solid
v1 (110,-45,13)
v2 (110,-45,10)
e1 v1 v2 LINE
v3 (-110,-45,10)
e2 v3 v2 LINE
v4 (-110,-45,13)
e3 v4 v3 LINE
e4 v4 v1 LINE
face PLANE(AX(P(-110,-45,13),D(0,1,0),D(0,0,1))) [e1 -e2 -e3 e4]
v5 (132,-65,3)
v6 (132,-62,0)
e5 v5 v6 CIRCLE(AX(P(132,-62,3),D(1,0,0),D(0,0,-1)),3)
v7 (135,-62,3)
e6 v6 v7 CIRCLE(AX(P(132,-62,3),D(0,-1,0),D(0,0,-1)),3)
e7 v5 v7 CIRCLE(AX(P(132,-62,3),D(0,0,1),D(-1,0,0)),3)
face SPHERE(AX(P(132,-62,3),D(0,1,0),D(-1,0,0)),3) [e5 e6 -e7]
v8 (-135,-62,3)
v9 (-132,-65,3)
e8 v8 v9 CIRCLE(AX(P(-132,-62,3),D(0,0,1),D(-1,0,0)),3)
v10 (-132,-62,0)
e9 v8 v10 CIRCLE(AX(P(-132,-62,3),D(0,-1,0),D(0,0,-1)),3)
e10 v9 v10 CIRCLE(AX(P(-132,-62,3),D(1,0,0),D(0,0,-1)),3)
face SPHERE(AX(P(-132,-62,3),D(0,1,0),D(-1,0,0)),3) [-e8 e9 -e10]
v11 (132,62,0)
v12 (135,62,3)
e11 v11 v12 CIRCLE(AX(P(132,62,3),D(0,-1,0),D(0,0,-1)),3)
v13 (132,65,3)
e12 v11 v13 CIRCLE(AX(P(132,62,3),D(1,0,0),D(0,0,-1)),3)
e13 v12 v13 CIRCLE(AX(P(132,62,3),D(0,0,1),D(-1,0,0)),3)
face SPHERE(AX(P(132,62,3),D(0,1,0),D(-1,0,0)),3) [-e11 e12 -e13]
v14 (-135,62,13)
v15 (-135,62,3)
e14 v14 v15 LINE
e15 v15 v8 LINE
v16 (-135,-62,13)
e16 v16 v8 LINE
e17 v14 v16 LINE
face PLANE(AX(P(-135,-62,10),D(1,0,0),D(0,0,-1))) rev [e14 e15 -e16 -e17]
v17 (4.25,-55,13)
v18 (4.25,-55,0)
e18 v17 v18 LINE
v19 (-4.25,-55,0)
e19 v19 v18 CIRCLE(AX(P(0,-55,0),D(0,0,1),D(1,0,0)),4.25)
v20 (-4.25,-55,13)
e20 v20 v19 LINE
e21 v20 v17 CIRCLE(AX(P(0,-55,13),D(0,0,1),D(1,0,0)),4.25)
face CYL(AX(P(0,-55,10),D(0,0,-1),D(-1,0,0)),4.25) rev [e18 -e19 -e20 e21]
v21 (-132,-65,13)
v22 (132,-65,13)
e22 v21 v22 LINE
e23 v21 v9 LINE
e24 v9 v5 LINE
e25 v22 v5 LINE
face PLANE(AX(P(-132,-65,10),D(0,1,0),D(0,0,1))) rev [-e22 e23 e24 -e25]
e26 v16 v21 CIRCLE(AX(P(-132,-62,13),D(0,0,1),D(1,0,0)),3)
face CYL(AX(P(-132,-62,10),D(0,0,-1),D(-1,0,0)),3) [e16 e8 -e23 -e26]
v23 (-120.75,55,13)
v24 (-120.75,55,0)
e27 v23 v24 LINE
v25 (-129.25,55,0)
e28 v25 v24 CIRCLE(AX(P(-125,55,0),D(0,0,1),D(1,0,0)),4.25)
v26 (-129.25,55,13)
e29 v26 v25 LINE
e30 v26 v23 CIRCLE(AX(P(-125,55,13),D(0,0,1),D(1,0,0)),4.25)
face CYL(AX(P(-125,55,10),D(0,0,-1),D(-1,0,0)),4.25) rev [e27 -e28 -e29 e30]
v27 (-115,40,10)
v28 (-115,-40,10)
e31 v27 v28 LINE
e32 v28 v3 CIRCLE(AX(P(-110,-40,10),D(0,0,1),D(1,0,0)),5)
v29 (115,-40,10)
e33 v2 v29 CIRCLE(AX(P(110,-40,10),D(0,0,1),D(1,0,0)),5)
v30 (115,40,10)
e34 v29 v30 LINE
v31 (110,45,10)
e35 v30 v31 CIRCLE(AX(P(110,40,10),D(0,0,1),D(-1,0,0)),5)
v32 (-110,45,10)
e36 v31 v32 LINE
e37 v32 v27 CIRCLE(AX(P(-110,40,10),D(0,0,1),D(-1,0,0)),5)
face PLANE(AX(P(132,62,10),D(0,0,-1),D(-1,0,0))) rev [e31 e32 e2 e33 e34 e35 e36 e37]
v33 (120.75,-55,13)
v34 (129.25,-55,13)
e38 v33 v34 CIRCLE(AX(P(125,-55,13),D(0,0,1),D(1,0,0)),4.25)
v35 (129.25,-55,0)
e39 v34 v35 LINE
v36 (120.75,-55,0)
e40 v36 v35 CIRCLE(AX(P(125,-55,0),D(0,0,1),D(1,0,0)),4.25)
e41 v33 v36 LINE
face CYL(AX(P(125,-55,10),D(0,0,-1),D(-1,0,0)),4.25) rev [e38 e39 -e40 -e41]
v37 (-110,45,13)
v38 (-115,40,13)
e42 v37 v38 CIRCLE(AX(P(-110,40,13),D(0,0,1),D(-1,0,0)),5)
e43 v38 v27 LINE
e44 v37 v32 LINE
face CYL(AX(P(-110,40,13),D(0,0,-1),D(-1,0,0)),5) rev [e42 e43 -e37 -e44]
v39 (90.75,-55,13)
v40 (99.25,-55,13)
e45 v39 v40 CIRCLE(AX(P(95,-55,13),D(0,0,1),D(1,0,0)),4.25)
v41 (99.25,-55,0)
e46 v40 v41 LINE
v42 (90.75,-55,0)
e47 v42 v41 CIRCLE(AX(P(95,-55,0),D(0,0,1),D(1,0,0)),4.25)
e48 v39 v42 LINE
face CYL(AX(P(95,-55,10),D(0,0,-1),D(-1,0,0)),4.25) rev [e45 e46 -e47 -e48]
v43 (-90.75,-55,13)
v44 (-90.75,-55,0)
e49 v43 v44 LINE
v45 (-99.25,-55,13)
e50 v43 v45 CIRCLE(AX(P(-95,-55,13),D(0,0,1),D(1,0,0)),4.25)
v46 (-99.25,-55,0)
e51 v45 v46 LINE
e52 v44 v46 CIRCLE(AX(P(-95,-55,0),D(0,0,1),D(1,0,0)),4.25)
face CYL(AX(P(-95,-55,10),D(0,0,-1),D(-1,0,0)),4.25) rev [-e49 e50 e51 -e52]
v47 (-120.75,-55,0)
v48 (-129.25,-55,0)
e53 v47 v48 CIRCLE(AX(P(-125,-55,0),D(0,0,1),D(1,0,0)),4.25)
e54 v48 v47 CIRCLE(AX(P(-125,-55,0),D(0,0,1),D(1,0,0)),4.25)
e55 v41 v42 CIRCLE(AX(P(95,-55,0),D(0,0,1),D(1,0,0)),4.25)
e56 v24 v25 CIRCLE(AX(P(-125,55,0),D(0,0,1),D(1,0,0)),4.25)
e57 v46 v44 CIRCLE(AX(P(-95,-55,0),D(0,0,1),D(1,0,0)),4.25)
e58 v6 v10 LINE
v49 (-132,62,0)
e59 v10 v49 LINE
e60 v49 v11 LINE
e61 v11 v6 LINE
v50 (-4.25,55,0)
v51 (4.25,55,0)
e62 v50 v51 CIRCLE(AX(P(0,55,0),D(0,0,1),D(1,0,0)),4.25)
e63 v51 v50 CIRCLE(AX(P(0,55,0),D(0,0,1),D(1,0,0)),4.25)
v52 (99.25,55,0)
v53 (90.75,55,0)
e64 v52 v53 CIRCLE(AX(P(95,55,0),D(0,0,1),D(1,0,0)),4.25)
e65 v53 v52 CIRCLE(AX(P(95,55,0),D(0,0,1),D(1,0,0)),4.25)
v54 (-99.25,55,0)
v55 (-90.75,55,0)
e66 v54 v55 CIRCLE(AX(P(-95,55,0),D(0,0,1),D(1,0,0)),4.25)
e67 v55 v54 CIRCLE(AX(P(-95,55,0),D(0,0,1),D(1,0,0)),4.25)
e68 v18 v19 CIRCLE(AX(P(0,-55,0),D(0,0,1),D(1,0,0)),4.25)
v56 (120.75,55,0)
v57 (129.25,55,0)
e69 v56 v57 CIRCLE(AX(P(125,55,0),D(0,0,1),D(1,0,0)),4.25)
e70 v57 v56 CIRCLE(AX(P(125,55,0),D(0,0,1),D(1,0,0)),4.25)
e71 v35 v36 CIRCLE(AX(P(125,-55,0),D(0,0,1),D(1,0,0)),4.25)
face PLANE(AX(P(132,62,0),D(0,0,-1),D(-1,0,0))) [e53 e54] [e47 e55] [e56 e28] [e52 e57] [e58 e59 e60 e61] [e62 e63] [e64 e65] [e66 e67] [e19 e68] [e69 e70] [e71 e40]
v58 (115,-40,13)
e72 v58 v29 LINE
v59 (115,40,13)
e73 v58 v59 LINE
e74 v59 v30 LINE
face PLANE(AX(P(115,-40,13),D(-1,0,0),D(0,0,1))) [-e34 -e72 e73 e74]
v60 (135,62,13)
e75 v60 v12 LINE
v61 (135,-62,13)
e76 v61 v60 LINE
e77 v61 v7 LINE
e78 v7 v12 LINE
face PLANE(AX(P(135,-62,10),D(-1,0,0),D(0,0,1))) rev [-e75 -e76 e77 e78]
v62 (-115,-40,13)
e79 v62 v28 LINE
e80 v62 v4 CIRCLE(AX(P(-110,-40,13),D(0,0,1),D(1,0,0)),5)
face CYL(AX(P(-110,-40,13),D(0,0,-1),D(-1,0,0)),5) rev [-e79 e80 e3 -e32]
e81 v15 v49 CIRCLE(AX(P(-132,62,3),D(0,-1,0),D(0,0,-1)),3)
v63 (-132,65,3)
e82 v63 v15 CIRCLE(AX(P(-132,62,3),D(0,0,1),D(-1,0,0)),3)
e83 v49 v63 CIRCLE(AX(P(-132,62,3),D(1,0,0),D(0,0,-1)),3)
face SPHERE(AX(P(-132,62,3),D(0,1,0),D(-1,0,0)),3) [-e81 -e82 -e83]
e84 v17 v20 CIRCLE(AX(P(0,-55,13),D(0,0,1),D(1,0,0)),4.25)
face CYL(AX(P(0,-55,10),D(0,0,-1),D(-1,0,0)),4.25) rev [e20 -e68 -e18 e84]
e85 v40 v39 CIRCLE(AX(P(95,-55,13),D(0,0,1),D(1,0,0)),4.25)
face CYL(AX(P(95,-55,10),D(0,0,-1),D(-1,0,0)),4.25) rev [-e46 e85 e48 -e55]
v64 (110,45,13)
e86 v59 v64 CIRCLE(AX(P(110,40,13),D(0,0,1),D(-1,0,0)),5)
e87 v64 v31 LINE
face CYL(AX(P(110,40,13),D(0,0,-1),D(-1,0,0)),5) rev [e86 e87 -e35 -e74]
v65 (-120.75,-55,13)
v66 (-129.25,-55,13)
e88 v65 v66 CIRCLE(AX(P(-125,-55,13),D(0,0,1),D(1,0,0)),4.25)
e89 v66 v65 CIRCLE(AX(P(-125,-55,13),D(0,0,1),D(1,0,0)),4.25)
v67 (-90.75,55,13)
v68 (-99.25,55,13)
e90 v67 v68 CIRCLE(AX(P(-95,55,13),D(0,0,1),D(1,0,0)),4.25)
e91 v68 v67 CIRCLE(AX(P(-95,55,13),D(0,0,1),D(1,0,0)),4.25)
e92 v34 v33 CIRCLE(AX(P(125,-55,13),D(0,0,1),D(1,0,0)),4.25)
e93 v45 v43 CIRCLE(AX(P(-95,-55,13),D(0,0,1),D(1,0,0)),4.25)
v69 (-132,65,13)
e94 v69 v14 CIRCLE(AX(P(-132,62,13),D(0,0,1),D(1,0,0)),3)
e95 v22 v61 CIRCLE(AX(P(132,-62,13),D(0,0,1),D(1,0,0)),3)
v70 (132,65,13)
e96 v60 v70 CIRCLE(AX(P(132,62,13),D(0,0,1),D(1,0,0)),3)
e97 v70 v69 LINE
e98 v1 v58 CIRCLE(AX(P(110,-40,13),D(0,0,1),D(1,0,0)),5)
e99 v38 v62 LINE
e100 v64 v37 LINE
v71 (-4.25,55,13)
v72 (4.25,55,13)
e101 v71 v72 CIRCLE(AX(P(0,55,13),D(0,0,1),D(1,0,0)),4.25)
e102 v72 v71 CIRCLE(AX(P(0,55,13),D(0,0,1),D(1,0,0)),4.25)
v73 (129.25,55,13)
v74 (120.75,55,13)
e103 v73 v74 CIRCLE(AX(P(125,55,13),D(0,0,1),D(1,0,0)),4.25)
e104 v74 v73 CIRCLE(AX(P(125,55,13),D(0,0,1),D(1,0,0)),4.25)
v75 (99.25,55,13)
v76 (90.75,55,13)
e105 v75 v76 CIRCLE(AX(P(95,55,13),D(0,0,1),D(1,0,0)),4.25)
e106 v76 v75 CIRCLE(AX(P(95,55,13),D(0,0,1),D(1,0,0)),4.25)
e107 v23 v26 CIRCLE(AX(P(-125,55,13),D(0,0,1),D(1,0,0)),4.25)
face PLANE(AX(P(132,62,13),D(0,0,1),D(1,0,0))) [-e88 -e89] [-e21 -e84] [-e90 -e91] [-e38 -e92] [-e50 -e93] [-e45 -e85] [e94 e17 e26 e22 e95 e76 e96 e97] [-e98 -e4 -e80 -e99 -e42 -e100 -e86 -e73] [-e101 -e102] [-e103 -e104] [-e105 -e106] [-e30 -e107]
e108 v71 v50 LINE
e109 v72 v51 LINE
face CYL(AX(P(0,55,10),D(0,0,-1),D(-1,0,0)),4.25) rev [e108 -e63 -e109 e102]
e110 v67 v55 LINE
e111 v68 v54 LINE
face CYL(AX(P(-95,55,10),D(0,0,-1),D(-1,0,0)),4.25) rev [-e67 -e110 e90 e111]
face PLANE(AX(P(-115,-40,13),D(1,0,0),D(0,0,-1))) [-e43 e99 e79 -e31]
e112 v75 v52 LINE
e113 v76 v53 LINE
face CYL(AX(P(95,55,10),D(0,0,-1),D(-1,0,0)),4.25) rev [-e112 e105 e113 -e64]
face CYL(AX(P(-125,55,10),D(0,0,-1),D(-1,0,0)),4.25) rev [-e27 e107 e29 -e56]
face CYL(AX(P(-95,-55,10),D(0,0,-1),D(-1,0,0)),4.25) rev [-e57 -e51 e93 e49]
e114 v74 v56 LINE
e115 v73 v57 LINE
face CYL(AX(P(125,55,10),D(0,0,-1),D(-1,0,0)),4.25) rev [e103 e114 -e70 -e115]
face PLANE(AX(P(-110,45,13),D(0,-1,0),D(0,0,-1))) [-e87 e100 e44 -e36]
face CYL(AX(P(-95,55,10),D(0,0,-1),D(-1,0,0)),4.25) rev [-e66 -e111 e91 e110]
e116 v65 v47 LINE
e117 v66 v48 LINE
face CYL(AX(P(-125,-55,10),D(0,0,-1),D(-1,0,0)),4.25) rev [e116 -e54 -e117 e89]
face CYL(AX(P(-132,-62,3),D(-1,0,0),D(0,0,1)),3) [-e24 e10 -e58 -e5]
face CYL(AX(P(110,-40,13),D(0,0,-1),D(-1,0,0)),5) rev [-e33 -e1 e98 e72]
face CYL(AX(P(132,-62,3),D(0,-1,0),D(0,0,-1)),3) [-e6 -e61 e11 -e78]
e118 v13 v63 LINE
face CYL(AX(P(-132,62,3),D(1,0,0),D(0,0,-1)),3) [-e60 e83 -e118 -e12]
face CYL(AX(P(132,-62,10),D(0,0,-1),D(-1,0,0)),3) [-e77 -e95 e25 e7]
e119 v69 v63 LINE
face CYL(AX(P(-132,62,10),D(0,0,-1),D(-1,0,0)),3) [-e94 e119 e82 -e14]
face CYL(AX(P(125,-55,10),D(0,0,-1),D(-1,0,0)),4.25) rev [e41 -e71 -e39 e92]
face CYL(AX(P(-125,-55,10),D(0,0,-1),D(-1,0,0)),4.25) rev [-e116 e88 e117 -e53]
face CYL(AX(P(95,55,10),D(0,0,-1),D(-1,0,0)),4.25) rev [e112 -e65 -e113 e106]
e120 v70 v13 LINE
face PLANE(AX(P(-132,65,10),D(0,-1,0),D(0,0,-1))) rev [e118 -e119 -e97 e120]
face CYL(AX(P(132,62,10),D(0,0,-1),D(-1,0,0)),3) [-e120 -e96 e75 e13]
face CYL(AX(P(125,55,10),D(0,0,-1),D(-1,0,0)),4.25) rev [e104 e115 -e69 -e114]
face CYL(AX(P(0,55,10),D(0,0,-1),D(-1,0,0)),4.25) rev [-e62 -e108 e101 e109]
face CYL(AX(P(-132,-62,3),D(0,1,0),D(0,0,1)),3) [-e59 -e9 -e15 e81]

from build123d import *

# Parameters (mm, degrees)
SKETCH_1_R      = 4.25
EXTRUDE_1_DEPTH = 10
SKETCH_2_R      = 4.25
EXTRUDE_2_DEPTH = 3
FILLET_1_R      = 3


with BuildPart() as part:
    # 草图1 → 凸台-拉伸1 (new body)
    with BuildSketch(Plane.XY):
        with BuildLine():
            Line((-132, -65), (132, -65))
            ThreePointArc((132, -65), (134.121320344, -64.121320344), (135, -62))
            Line((135, -62), (135, 62))
            ThreePointArc((135, 62), (134.121320344, 64.121320344), (132, 65))
            Line((132, 65), (-132, 65))
            ThreePointArc((-132, 65), (-134.121320344, 64.121320344), (-135, 62))
            Line((-135, 62), (-135, -62))
            ThreePointArc((-135, -62), (-134.121320344, -64.121320344), (-132, -65))
        make_face()
        with Locations((-125, 55)):
            Circle(SKETCH_1_R, mode=Mode.SUBTRACT)
        with Locations((-95, 55)):
            Circle(SKETCH_1_R, mode=Mode.SUBTRACT)
        with Locations((0, 55)):
            Circle(SKETCH_1_R, mode=Mode.SUBTRACT)
        with Locations((95, 55)):
            Circle(SKETCH_1_R, mode=Mode.SUBTRACT)
        with Locations((125, 55)):
            Circle(SKETCH_1_R, mode=Mode.SUBTRACT)
        with Locations((125, -55)):
            Circle(SKETCH_1_R, mode=Mode.SUBTRACT)
        with Locations((95, -55)):
            Circle(SKETCH_1_R, mode=Mode.SUBTRACT)
        with Locations((0, -55)):
            Circle(SKETCH_1_R, mode=Mode.SUBTRACT)
        with Locations((-95, -55)):
            Circle(SKETCH_1_R, mode=Mode.SUBTRACT)
        with Locations((-125, -55)):
            Circle(SKETCH_1_R, mode=Mode.SUBTRACT)
    extrude(amount=EXTRUDE_1_DEPTH)

    # 草图2 → 凸台-拉伸2 (add)
    with BuildSketch(Plane.XY.offset(10)):
        with BuildLine():
            Line((132, 65), (-132, 65))
            ThreePointArc((-132, 65), (-134.121320344, 64.121320344), (-135, 62))
            Line((-135, 62), (-135, -62))
            ThreePointArc((-135, -62), (-134.121320344, -64.121320344), (-132, -65))
            Line((-132, -65), (132, -65))
            ThreePointArc((132, -65), (134.121320344, -64.121320344), (135, -62))
            Line((135, -62), (135, 62))
            ThreePointArc((135, 62), (134.121320344, 64.121320344), (132, 65))
        make_face()
        with Locations((-125, -55)):
            Circle(SKETCH_2_R, mode=Mode.SUBTRACT)
        with Locations((-95, -55)):
            Circle(SKETCH_2_R, mode=Mode.SUBTRACT)
        with Locations((0, -55)):
            Circle(SKETCH_2_R, mode=Mode.SUBTRACT)
        with Locations((95, -55)):
            Circle(SKETCH_2_R, mode=Mode.SUBTRACT)
        with Locations((125, -55)):
            Circle(SKETCH_2_R, mode=Mode.SUBTRACT)
        with Locations((125, 55)):
            Circle(SKETCH_2_R, mode=Mode.SUBTRACT)
        with Locations((95, 55)):
            Circle(SKETCH_2_R, mode=Mode.SUBTRACT)
        with Locations((0, 55)):
            Circle(SKETCH_2_R, mode=Mode.SUBTRACT)
        with Locations((-95, 55)):
            Circle(SKETCH_2_R, mode=Mode.SUBTRACT)
        with Locations((-125, 55)):
            Circle(SKETCH_2_R, mode=Mode.SUBTRACT)
        with BuildLine():
            Line((-110, -45), (110, -45))
            ThreePointArc((110, -45), (113.535533906, -43.535533906), (115, -40))
            Line((115, -40), (115, 40))
            ThreePointArc((115, 40), (113.535533906, 43.535533906), (110, 45))
            Line((110, 45), (-110, 45))
            ThreePointArc((-110, 45), (-113.535533906, 43.535533906), (-115, 40))
            Line((-115, 40), (-115, -40))
            ThreePointArc((-115, -40), (-113.535533906, -43.535533906), (-110, -45))
        make_face(mode=Mode.SUBTRACT)
    extrude(amount=EXTRUDE_2_DEPTH)

    # 圆角1
    fillet_1_edges = [part.edges().sort_by_distance(p)[0] for p in [
        (0, 65, 0),
        (134.121320344, 64.121320344, 0),
        (135, 0, 0),
        (134.121320344, -64.121320344, 0),
        (0, -65, 0),
        (-134.121320344, -64.121320344, 0),
        (-135, 0, 0),
        (-134.121320344, 64.121320344, 0),
    ]]
    fillet(fillet_1_edges, radius=FILLET_1_R)


solid = part.part
